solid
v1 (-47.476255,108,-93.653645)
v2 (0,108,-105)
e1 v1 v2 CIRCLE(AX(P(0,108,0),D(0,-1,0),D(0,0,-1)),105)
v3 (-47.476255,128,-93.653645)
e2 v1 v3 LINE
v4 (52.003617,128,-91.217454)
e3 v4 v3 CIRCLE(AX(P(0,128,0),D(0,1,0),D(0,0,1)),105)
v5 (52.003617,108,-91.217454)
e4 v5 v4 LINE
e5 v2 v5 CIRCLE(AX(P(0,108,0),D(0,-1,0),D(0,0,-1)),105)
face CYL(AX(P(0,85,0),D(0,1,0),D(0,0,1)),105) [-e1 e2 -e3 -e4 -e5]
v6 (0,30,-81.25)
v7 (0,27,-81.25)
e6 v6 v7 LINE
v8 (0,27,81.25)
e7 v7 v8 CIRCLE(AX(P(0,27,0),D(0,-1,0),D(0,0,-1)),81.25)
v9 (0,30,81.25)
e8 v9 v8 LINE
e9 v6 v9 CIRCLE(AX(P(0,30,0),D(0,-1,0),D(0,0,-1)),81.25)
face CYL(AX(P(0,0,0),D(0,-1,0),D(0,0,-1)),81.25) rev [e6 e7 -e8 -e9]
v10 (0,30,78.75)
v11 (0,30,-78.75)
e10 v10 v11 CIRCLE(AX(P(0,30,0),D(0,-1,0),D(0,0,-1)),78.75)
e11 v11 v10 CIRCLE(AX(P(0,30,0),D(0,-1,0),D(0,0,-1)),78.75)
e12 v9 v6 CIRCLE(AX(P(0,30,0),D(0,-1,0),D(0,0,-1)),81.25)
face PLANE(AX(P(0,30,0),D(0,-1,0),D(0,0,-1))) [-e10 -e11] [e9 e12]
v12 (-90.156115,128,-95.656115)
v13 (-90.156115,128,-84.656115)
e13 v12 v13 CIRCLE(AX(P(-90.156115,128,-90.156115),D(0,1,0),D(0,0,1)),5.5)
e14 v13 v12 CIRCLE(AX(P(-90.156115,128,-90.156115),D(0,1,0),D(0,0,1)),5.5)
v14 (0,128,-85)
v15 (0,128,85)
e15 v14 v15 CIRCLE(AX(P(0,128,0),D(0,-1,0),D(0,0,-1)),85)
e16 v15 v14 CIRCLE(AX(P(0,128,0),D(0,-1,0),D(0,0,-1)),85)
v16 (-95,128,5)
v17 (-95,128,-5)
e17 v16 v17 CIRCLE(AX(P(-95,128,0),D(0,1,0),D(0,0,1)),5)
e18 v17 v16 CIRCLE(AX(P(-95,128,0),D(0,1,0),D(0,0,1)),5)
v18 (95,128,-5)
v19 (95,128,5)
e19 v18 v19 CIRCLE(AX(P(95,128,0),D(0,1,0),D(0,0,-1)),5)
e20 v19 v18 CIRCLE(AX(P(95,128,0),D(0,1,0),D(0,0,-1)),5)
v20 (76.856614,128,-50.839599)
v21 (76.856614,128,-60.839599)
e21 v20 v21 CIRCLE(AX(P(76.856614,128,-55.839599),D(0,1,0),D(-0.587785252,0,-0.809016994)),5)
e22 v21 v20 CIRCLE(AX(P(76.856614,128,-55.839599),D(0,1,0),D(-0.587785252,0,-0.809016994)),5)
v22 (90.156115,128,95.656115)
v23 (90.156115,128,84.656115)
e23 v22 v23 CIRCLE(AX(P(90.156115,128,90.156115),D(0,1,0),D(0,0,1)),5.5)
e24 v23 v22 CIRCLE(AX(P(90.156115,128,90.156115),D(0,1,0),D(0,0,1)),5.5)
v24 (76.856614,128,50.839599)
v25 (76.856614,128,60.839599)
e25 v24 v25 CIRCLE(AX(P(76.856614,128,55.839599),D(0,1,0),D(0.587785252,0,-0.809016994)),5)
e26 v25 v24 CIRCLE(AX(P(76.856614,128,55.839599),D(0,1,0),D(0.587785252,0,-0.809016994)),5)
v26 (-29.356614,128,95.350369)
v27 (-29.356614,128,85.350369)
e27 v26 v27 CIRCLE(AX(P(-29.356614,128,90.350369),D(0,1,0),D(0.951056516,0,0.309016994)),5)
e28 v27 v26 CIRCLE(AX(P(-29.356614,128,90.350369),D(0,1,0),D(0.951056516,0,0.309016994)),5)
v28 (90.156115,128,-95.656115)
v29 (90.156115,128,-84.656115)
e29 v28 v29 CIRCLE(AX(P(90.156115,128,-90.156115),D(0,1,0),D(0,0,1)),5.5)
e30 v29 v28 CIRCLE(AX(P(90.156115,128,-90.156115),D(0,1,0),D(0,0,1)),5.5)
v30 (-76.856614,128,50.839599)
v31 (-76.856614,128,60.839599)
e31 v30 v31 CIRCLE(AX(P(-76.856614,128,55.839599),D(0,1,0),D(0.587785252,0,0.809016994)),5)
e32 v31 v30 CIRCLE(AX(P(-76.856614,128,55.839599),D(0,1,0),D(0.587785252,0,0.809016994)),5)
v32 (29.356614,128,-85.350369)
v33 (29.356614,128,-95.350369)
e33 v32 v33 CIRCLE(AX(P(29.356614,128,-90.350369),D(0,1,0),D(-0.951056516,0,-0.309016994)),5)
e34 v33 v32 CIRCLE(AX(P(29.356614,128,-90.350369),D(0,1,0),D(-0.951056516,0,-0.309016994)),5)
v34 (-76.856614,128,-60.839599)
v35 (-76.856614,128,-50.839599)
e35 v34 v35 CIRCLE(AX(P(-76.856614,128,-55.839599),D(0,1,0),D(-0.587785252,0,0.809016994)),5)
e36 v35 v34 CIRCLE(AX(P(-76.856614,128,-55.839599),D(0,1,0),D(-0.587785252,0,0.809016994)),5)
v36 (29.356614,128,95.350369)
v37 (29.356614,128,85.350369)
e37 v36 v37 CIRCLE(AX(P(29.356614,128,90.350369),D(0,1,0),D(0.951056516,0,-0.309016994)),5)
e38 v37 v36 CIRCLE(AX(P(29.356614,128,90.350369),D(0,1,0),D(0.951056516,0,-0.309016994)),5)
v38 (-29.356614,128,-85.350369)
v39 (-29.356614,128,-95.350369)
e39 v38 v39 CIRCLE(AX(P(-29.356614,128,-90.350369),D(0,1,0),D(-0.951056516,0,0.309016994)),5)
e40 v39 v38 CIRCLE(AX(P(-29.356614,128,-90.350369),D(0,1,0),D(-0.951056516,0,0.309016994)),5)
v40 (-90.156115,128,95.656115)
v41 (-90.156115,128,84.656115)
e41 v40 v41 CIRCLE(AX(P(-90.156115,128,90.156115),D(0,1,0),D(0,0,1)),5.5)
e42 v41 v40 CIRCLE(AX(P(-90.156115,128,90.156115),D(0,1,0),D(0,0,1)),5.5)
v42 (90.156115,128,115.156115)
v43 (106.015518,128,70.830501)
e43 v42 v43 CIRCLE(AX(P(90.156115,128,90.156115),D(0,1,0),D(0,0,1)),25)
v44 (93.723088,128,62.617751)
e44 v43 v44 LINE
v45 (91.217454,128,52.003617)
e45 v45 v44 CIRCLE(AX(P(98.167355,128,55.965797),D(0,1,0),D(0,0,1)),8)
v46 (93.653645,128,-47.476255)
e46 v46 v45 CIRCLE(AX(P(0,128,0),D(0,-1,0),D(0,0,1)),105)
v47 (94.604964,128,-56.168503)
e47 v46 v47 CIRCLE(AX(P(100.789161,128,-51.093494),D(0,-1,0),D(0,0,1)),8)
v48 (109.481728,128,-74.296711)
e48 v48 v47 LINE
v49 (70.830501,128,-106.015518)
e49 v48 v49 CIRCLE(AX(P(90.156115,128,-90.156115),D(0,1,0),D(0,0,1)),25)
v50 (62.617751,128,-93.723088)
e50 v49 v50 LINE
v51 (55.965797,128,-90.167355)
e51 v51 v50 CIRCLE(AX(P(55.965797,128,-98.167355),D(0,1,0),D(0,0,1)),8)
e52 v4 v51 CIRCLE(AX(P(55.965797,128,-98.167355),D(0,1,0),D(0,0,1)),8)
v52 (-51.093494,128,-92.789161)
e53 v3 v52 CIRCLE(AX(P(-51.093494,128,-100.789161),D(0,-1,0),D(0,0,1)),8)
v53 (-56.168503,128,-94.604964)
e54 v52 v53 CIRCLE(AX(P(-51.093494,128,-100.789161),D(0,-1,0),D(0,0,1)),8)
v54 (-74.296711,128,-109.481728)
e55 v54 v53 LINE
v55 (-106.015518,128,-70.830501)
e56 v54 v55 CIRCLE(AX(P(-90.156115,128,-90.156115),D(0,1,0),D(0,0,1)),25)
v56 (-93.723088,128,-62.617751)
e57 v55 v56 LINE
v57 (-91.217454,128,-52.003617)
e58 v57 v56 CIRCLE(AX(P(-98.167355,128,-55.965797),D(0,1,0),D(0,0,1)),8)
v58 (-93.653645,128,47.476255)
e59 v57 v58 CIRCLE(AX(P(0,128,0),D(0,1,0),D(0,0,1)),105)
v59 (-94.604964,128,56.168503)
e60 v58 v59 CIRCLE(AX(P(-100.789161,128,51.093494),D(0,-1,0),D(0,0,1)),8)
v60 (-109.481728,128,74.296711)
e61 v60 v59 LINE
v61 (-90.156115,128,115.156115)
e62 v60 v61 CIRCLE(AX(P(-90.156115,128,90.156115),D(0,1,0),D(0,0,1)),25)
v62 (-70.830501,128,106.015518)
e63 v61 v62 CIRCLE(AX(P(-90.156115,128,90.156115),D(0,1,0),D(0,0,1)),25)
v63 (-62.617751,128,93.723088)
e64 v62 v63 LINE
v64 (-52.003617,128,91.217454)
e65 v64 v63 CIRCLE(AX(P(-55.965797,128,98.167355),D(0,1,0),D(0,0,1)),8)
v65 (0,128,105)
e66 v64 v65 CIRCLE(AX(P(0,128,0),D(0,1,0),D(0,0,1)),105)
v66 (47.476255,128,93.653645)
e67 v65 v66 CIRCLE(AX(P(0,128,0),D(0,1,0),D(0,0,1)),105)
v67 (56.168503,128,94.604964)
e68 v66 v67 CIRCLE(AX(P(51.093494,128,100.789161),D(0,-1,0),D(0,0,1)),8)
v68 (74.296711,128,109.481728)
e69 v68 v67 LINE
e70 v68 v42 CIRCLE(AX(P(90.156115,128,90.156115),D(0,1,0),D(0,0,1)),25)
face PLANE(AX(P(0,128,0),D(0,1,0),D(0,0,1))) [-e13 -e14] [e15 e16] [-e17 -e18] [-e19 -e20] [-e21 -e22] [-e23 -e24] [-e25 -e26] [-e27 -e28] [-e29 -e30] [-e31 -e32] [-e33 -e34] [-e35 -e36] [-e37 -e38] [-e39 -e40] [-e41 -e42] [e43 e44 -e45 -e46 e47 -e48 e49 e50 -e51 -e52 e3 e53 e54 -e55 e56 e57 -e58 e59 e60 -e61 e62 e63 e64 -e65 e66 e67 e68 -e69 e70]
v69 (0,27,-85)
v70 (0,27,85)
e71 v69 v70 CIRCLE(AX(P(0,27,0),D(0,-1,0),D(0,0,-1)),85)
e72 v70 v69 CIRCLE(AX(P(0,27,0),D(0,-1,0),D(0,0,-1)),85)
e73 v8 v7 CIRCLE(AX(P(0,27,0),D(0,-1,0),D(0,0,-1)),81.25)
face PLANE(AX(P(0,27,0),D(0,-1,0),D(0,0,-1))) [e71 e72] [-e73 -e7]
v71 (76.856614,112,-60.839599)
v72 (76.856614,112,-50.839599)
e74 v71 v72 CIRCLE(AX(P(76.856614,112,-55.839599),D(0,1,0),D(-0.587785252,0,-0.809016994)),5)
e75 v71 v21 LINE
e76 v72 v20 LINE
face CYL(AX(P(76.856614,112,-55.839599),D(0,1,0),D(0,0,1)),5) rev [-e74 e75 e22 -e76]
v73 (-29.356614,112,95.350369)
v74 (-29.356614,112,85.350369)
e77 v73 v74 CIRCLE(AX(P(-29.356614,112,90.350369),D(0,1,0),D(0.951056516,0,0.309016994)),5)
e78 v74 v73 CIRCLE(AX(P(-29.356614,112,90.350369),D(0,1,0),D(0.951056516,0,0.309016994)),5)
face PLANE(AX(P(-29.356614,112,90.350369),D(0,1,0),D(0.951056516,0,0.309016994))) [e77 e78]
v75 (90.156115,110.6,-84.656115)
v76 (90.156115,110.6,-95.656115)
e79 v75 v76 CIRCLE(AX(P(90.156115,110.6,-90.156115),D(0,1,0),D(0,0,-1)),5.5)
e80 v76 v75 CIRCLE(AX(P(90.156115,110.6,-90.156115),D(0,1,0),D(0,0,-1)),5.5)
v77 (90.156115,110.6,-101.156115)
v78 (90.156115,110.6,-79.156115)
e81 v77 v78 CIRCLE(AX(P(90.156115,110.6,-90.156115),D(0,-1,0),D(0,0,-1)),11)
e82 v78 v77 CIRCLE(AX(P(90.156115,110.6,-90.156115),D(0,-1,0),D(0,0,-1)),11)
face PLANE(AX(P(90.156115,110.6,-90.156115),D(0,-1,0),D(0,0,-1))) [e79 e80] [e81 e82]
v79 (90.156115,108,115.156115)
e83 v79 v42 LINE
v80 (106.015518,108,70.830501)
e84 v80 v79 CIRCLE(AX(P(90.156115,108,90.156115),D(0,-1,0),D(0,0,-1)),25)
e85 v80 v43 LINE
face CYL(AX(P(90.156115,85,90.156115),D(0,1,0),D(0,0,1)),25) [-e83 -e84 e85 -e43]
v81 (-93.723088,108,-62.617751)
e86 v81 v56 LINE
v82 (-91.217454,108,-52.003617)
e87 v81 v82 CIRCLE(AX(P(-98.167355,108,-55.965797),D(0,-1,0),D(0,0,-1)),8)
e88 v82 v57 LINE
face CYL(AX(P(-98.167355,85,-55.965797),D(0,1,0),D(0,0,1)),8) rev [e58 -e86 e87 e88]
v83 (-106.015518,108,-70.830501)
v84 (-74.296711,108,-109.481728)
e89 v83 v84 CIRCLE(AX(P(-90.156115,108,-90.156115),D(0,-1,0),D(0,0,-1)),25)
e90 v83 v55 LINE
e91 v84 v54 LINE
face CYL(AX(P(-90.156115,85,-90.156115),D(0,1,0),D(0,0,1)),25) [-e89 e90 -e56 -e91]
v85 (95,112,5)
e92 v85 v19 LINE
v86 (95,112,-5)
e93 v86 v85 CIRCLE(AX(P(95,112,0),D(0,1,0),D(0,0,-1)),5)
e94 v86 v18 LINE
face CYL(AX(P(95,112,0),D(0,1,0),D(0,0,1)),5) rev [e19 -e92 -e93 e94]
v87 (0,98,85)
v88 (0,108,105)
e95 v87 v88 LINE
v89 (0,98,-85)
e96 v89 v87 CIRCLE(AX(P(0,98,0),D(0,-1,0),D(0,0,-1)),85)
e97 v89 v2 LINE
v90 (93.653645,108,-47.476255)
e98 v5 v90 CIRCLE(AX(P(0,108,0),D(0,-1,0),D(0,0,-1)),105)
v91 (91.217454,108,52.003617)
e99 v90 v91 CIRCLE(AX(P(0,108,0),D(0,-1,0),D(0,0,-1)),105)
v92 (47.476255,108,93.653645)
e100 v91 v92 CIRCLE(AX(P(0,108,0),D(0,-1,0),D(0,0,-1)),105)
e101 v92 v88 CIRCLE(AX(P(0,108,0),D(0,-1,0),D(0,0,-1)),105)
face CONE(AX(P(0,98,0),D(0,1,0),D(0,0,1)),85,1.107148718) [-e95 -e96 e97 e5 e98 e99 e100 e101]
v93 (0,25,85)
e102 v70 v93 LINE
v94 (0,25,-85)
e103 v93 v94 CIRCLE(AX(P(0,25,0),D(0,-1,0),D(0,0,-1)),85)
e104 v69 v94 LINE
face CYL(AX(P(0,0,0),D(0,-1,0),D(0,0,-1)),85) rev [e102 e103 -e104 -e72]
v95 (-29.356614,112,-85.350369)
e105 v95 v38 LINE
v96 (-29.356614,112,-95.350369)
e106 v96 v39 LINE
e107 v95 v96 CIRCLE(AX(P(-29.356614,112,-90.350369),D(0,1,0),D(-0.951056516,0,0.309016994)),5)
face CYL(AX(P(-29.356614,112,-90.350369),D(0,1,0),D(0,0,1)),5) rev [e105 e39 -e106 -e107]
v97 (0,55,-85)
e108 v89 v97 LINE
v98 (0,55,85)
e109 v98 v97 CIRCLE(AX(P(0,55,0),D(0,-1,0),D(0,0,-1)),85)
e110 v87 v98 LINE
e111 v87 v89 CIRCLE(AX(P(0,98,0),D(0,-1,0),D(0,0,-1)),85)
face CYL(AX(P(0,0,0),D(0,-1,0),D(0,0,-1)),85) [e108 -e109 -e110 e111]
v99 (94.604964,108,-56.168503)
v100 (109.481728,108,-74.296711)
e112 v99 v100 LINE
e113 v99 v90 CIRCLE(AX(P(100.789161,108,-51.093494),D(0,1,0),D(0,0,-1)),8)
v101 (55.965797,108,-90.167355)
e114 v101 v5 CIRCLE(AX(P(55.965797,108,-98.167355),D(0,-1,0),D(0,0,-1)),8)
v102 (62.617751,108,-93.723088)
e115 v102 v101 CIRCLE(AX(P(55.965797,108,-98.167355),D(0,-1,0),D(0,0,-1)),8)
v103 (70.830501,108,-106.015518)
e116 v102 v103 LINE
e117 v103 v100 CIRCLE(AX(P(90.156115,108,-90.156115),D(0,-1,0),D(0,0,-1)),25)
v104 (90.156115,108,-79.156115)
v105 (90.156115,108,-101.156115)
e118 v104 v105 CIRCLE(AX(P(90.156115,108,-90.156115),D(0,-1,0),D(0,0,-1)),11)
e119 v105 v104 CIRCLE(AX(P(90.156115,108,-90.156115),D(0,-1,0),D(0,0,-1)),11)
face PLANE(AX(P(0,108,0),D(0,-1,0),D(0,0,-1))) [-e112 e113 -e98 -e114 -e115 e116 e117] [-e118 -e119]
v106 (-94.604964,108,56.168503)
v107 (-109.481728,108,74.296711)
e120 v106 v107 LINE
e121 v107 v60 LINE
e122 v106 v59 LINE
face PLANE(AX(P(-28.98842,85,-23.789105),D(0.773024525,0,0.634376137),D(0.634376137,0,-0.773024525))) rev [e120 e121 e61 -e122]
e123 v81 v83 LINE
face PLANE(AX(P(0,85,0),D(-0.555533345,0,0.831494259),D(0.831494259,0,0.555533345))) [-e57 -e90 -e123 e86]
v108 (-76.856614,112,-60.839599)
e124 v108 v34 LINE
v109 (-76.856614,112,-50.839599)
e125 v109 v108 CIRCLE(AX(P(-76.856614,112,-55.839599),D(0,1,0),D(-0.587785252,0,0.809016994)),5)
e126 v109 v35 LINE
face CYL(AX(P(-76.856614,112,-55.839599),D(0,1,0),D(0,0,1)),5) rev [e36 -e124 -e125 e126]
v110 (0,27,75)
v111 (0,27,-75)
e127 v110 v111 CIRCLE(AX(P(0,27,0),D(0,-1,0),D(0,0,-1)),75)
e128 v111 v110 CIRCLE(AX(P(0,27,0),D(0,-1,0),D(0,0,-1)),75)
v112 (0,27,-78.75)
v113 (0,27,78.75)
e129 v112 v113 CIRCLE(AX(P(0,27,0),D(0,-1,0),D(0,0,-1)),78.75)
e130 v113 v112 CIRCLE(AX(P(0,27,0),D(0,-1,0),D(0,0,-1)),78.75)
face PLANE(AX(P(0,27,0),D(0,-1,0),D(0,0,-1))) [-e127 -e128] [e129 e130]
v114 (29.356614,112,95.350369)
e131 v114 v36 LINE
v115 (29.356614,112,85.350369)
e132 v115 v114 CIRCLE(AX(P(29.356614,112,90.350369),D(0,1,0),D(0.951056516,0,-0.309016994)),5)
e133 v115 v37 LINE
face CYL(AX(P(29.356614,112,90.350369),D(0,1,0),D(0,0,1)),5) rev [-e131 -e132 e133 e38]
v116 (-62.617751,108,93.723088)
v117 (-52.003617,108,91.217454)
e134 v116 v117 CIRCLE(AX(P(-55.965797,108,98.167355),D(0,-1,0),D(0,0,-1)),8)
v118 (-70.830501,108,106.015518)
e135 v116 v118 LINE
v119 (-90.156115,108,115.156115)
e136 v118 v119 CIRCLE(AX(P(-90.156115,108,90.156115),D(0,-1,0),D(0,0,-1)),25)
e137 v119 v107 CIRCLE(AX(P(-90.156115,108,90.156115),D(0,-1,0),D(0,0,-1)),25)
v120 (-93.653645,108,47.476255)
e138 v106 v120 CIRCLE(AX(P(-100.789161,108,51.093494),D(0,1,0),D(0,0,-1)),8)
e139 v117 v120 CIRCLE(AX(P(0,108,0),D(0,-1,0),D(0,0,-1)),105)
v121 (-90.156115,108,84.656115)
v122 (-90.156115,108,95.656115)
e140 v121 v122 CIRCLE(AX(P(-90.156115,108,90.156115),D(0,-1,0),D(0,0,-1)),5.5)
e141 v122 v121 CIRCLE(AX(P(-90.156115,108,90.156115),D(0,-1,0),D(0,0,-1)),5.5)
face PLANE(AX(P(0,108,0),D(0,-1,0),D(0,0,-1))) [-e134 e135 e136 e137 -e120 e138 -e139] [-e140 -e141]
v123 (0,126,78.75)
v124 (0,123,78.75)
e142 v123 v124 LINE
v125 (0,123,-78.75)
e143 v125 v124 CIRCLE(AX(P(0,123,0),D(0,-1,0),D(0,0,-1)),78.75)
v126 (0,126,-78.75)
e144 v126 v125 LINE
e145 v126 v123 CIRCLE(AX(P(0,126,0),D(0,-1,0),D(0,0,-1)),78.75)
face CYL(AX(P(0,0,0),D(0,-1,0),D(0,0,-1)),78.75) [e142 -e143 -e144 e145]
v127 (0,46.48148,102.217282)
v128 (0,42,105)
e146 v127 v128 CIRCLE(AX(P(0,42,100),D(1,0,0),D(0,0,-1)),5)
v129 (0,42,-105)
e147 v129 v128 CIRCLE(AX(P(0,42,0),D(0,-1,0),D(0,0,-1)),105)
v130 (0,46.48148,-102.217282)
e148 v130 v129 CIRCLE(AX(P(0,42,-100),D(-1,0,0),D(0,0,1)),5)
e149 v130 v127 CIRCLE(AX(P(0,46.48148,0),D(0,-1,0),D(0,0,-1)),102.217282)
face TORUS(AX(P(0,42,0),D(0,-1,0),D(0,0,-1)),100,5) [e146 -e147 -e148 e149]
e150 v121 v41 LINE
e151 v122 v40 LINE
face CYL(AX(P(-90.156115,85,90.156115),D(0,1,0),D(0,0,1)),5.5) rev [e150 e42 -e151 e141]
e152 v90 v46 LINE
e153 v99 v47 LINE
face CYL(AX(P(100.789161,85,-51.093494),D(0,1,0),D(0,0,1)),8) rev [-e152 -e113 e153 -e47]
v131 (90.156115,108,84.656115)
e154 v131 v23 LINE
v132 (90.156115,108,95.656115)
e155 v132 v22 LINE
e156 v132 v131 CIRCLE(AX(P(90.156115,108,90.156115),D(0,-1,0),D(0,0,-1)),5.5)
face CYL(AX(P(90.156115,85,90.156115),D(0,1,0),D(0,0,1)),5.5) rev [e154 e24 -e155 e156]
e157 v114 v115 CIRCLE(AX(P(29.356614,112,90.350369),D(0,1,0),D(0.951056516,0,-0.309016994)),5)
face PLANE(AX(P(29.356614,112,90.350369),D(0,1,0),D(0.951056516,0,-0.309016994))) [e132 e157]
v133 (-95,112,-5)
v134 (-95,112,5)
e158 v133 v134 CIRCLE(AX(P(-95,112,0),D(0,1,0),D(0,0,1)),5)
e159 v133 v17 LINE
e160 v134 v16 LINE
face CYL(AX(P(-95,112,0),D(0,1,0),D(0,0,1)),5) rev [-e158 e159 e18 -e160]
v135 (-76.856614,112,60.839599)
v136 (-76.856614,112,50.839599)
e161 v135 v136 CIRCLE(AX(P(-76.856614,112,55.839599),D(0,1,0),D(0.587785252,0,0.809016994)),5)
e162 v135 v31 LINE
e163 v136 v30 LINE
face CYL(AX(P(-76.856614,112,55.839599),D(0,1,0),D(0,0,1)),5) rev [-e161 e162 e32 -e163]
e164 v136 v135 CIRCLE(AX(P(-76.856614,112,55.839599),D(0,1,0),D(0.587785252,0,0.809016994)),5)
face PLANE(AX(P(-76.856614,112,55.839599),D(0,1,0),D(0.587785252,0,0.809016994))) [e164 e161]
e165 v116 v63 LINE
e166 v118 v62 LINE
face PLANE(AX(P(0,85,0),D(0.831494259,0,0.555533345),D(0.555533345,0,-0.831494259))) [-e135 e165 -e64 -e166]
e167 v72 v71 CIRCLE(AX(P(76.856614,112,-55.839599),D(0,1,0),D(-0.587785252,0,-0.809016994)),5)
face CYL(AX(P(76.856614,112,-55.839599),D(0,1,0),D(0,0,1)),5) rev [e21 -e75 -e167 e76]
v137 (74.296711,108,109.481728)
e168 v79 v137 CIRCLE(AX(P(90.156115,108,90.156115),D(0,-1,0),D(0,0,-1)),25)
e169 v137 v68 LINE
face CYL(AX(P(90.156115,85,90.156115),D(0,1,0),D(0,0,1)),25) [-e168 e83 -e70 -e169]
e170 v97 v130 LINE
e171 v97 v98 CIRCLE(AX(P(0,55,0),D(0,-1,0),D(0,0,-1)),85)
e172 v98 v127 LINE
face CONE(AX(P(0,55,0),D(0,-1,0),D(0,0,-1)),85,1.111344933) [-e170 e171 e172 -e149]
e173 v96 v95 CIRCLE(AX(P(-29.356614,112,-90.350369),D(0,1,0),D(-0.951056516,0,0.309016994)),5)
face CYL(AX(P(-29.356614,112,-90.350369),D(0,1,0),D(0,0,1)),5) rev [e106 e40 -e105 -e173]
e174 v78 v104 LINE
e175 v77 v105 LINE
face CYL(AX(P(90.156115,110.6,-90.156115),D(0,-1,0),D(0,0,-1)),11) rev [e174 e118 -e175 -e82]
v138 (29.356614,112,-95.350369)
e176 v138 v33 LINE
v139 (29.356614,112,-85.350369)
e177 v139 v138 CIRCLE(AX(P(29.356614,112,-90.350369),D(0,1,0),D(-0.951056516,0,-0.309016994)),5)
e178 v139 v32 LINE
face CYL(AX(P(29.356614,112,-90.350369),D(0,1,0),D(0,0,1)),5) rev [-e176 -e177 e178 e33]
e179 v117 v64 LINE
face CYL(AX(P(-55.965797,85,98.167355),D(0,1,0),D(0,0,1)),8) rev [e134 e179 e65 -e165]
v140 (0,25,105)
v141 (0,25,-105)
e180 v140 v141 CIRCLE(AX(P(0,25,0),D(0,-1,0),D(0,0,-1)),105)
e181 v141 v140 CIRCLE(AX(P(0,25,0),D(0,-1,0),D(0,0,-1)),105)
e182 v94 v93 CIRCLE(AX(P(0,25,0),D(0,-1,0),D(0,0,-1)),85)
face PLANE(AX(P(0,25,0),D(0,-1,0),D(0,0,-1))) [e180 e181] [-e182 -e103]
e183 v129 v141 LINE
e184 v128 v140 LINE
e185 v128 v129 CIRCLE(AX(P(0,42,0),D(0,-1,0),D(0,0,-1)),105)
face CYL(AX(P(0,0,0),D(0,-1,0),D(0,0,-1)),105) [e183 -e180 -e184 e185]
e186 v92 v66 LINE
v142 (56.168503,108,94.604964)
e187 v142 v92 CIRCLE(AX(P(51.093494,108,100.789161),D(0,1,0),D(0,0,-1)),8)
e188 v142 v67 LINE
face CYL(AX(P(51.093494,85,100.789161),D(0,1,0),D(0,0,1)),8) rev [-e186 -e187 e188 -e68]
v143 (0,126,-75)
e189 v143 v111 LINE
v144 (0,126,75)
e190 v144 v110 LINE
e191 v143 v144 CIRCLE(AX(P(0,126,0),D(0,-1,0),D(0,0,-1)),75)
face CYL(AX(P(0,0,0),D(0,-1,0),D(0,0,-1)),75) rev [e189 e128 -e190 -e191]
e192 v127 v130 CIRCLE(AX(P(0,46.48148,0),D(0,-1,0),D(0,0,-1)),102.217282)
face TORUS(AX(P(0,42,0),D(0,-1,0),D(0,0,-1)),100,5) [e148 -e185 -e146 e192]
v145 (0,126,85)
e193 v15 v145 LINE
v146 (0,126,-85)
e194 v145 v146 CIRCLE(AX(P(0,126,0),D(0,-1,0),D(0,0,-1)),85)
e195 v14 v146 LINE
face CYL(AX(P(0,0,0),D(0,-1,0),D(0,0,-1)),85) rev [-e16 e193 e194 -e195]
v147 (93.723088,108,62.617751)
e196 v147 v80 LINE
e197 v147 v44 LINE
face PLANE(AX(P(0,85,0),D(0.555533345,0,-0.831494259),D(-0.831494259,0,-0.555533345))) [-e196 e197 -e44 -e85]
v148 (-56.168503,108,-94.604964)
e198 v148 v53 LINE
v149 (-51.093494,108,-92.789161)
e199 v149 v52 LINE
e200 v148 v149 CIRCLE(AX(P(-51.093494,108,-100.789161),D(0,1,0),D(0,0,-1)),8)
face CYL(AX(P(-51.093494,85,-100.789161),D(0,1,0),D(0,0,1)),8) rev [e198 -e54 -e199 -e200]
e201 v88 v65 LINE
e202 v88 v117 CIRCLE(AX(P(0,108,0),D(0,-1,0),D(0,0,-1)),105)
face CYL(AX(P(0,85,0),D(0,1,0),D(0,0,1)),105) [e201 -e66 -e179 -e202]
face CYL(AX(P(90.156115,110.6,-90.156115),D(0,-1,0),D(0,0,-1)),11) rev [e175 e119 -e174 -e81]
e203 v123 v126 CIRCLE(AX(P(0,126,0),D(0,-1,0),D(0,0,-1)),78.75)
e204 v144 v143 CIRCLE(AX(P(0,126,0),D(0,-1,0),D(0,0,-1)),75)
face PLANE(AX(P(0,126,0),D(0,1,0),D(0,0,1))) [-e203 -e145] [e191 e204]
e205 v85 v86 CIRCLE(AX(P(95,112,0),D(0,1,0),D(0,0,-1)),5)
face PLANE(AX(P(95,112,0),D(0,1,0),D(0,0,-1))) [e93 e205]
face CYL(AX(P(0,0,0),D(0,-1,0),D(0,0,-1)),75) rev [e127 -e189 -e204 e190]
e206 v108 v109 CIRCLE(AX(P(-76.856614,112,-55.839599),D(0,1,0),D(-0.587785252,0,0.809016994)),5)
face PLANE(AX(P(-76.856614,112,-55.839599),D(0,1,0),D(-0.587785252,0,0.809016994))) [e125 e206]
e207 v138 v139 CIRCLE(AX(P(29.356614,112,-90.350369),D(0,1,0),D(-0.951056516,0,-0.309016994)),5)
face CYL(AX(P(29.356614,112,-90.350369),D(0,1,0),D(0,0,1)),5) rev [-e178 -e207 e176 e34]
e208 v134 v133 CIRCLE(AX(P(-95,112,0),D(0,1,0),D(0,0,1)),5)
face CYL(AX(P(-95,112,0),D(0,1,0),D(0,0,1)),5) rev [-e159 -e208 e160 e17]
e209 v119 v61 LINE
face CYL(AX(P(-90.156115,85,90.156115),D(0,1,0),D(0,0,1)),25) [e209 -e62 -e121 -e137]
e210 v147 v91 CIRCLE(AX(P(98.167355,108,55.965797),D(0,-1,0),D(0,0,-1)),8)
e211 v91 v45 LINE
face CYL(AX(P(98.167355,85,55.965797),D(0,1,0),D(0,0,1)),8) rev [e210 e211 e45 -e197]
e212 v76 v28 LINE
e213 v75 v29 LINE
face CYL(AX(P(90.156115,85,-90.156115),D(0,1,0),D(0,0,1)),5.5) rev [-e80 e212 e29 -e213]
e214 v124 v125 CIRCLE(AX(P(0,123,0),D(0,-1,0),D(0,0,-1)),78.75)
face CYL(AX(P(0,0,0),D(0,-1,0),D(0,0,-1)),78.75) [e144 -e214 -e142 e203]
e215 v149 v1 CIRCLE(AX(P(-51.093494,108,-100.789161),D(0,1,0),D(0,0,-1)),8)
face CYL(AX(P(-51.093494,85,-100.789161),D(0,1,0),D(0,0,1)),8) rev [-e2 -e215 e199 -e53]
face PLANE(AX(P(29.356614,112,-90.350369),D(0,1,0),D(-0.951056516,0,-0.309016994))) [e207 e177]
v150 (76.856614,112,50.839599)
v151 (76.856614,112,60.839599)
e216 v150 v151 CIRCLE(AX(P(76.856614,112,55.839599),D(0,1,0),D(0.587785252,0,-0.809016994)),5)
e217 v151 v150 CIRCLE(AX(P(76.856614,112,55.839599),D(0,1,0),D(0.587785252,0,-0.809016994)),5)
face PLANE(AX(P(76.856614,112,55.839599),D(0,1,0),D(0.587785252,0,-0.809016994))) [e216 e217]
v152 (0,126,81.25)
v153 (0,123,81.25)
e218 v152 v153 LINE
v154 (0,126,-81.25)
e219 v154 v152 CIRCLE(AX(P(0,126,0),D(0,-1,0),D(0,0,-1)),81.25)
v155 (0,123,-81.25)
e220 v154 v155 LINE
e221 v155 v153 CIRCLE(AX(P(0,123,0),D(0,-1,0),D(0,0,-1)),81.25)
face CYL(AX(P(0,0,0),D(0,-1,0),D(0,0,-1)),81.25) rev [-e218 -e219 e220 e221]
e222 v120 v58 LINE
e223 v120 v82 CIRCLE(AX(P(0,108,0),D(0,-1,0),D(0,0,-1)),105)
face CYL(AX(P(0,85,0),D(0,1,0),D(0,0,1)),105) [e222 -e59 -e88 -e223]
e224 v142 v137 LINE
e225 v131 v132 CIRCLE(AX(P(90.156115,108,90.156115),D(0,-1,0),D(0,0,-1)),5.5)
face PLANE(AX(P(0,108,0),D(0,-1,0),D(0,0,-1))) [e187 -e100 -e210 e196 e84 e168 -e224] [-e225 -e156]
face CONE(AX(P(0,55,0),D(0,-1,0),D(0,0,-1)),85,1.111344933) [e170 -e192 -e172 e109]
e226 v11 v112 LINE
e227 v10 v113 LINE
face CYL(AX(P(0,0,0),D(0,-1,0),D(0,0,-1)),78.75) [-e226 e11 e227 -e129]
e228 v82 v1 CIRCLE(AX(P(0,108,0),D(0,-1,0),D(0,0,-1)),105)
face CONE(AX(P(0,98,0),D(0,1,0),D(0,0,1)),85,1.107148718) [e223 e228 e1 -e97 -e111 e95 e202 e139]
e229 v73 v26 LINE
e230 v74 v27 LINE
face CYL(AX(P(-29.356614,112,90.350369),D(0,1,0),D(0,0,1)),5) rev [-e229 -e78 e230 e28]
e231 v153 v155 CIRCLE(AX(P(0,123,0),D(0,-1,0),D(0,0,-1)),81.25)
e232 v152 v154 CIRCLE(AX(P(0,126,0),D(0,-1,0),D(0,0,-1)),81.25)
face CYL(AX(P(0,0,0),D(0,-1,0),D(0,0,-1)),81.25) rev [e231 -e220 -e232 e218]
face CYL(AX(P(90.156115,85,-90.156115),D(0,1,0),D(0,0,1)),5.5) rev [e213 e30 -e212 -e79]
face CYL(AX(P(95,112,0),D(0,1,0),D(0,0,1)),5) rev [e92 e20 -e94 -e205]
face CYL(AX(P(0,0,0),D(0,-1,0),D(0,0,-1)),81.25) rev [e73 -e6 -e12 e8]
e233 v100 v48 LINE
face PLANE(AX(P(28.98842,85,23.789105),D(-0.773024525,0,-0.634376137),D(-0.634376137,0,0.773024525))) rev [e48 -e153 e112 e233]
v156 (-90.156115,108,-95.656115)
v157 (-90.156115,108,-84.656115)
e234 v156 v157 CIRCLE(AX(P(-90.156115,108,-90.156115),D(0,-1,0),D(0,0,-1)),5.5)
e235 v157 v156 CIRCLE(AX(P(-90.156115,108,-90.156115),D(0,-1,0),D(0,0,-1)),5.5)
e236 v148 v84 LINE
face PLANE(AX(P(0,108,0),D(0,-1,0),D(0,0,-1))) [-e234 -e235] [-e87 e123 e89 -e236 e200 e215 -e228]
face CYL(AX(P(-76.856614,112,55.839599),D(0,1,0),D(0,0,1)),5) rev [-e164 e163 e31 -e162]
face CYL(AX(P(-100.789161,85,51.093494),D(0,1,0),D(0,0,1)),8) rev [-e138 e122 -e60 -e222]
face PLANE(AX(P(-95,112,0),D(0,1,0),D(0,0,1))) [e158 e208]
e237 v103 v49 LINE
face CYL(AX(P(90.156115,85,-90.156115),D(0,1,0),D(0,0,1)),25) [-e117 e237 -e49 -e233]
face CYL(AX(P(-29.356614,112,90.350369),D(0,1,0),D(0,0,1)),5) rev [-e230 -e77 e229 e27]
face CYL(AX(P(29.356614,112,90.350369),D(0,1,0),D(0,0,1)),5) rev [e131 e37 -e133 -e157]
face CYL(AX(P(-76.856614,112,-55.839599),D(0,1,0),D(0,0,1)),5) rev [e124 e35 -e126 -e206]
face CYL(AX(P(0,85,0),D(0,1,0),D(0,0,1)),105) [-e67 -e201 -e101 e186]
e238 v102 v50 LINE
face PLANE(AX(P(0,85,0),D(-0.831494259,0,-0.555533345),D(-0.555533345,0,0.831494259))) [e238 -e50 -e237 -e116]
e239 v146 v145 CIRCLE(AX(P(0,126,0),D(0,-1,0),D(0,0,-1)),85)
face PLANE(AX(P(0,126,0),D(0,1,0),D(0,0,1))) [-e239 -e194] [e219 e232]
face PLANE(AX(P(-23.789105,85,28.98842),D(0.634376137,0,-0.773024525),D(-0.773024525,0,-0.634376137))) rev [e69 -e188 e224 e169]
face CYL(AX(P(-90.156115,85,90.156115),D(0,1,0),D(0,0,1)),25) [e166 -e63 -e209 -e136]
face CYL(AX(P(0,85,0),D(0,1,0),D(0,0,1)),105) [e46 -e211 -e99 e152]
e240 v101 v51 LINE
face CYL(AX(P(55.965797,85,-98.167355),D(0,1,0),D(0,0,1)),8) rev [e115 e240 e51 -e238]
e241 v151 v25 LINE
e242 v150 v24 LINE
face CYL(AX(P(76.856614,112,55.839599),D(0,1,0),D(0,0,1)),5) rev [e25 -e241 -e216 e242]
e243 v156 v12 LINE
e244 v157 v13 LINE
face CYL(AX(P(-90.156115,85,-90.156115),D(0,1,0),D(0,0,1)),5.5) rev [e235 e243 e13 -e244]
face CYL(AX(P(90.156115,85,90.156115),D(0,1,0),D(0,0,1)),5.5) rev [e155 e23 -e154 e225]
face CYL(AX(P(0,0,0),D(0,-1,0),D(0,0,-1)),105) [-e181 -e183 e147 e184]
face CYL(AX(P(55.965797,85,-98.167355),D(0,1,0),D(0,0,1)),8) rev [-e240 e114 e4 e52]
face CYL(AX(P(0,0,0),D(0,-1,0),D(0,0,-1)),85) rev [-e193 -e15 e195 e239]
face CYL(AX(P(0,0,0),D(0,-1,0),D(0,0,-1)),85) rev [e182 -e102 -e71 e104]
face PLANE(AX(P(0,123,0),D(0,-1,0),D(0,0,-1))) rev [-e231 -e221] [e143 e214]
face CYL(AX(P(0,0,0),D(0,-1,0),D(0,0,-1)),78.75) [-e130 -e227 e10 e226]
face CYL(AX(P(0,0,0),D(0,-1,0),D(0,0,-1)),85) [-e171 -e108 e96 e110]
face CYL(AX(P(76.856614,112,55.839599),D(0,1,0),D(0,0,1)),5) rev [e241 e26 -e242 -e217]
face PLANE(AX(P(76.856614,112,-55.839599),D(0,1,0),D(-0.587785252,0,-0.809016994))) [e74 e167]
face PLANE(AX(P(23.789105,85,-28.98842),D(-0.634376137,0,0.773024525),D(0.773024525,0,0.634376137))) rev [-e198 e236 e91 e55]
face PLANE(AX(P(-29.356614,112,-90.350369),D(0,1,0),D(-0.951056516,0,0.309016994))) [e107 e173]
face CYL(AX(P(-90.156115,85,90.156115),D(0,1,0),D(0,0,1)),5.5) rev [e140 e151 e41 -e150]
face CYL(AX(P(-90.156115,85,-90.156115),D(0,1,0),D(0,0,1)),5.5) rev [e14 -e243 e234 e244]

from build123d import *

# Parameters (mm, degrees)
SKETCH_2_OUTSIDE_W       = 395.692
SKETCH_2_OUTSIDE_H       = 395.692
CUT_EXTRUDE_1_DEPTH      = 43
SKETCH_2_3_R             = 5.5
SKETCH_2_3_R_2           = 4
CUT_EXTRUDE_2_DEPTH      = 43
SKETCH_3_R               = 5
CUT_EXTRUDE_4_DEPTH      = 16
PATTERN_CIRCULAR_2_COUNT = 10
SKETCH_22_R              = 11
CUT_EXTRUDE_13_DEPTH     = 2.6
CUT_EXTRUDE_17_DEPTH     = 47.2


with BuildPart() as part:
    # 草图1 → 旋转1 (revolve)
    with BuildSketch(Plane(origin=(0, 0, 0), x_dir=(0, 0, -1), z_dir=(1, 0, 0))):
        with BuildLine():
            Line((85, 98), (85, 55))
            Line((85, 55), (102.2172823, 46.481479577))
            ThreePointArc((102.2172823, 46.481479577), (104.247729482, 44.637573553), (105, 42))
            Line((105, 42), (105, 25))
            Line((105, 25), (85, 25))
            Line((85, 25), (85, 27))
            Line((85, 27), (81.25, 27))
            Line((81.25, 27), (81.25, 30))
            Line((81.25, 30), (78.75, 30))
            Line((78.75, 30), (78.75, 27))
            Line((78.75, 27), (75, 27))
            Line((75, 27), (75, 126))
            Line((75, 126), (78.75, 126))
            Line((78.75, 126), (78.75, 123))
            Line((78.75, 123), (80, 123))
            Line((80, 123), (81.25, 123))
            Line((81.25, 123), (81.25, 126))
            Line((81.25, 126), (85, 126))
            Line((85, 126), (85, 128))
            Line((85, 128), (152.5, 128))
            Line((152.5, 128), (152.5, 108))
            Line((152.5, 108), (105, 108))
            Line((105, 108), (85, 98))
        make_face()
    revolve(axis=Axis((0, 0, 0), (0, 1, 0)))

    # 草图2 outside → 切除-拉伸1 (cut)
    with BuildSketch(Plane(origin=(0, 128, 0), x_dir=(1, 0, 0), z_dir=(0, 1, 0))):
        Rectangle(SKETCH_2_OUTSIDE_W, SKETCH_2_OUTSIDE_H)
        with BuildLine():
            Line((106.015518025, -70.830501466), (93.723088078, -62.617751167))
            ThreePointArc((93.723088078, -62.617751167), (90.381359185, -57.803804637), (91.217453609, -52.003616769))
            ThreePointArc((91.217453609, -52.003616769), (96.412361456, -41.589139911), (100.422788605, -30.663716814))
            ThreePointArc((100.422788605, -30.663716814), (103.31433575, -26.569981902), (108.074048689, -25))
            Line((108.074048689, -25), (127.5, -25))
            ThreePointArc((127.5, -25), (152.5, 0), (127.5, 25))
            Line((127.5, 25), (108.074048689, 25))
            ThreePointArc((108.074048689, 25), (103.31433575, 26.569981902), (100.422788605, 30.663716814))
            ThreePointArc((100.422788605, 30.663716814), (97.401647161, 39.216312045), (93.653644879, 47.476255126))
            ThreePointArc((93.653644879, 47.476255126), (92.836646991, 51.963853326), (94.604964476, 56.168502708))
            Line((94.604964476, 56.168502708), (109.481727736, 74.296711178))
            ThreePointArc((109.481727736, 74.296711178), (106.015518025, 109.481727736), (70.830501466, 106.015518025))
            Line((70.830501466, 106.015518025), (62.617751167, 93.723088078))
            ThreePointArc((62.617751167, 93.723088078), (57.803804637, 90.381359185), (52.003616769, 91.217453609))
            ThreePointArc((52.003616769, 91.217453609), (2.570604567, 104.96852858), (-47.476255126, 93.653644879))
            ThreePointArc((-47.476255126, 93.653644879), (-51.963853326, 92.836646991), (-56.168502708, 94.604964476))
            Line((-56.168502708, 94.604964476), (-74.296711178, 109.481727736))
            ThreePointArc((-74.296711178, 109.481727736), (-109.481727736, 106.015518025), (-106.015518025, 70.830501466))
            Line((-106.015518025, 70.830501466), (-93.723088078, 62.617751167))
            ThreePointArc((-93.723088078, 62.617751167), (-90.381359185, 57.803804637), (-91.217453609, 52.003616769))
            ThreePointArc((-91.217453609, 52.003616769), (-96.412361456, 41.589139911), (-100.422788605, 30.663716814))
            ThreePointArc((-100.422788605, 30.663716814), (-103.31433575, 26.569981902), (-108.074048689, 25))
            Line((-108.074048689, 25), (-127.5, 25))
            ThreePointArc((-127.5, 25), (-152.5, 0), (-127.5, -25))
            Line((-127.5, -25), (-108.074048689, -25))
            ThreePointArc((-108.074048689, -25), (-103.31433575, -26.569981902), (-100.422788605, -30.663716814))
            ThreePointArc((-100.422788605, -30.663716814), (-97.401647161, -39.216312045), (-93.653644879, -47.476255126))
            ThreePointArc((-93.653644879, -47.476255126), (-92.836646991, -51.963853326), (-94.604964476, -56.168502708))
            Line((-94.604964476, -56.168502708), (-109.481727736, -74.296711178))
            ThreePointArc((-109.481727736, -74.296711178), (-106.015518025, -109.481727736), (-70.830501466, -106.015518025))
            Line((-70.830501466, -106.015518025), (-62.617751167, -93.723088078))
            ThreePointArc((-62.617751167, -93.723088078), (-57.803804637, -90.381359185), (-52.003616769, -91.217453609))
            ThreePointArc((-52.003616769, -91.217453609), (-2.570604567, -104.96852858), (47.476255126, -93.653644879))
            ThreePointArc((47.476255126, -93.653644879), (51.963853326, -92.836646991), (56.168502708, -94.604964476))
            Line((56.168502708, -94.604964476), (74.296711178, -109.481727736))
            ThreePointArc((74.296711178, -109.481727736), (109.481727736, -106.015518025), (106.015518025, -70.830501466))
        make_face(mode=Mode.SUBTRACT)
    extrude(amount=-CUT_EXTRUDE_1_DEPTH, mode=Mode.SUBTRACT)

    # 草图2<3> → 切除-拉伸2 (cut)
    with BuildSketch(Plane(origin=(0, 128, 0), x_dir=(1, 0, 0), z_dir=(0, 1, 0))):
        with Locations(Location((90.156114601, -90.156114601, 0), (0, 0, 270))):
            Circle(SKETCH_2_3_R)
        with Locations(Location((-90.156114601, -90.156114601, 0), (0, 0, 270))):
            Circle(SKETCH_2_3_R)
        with Locations(Location((-90.156114601, 90.156114601, 0), (0, 0, 270))):
            Circle(SKETCH_2_3_R)
        with Locations(Location((90.156114601, 90.156114601, 0), (0, 0, 270))):
            Circle(SKETCH_2_3_R)
        with Locations(Location((-127.5, 0, 0), (0, 0, 270))):
            Circle(SKETCH_2_3_R_2)
        with Locations(Location((127.5, 0, 0), (0, 0, 270))):
            Circle(SKETCH_2_3_R_2)
    extrude(amount=-CUT_EXTRUDE_2_DEPTH, mode=Mode.SUBTRACT)

    # 草图3 → 切除-拉伸4 (cut)
    with BuildSketch(Plane(origin=(0, 128, 0), x_dir=(1, 0, 0), z_dir=(0, 1, 0))):
        with Locations(Location((-95, 0, 0), (0, 0, 270))):
            Circle(SKETCH_3_R)
    cut_extrude_4 = extrude(amount=-CUT_EXTRUDE_4_DEPTH, mode=Mode.SUBTRACT)

    # 阵列(圆周)2: 切除-拉伸4 ×10 about axis
    pattern_circular_2_axis = Axis((0, 0, 0), (0, 1, 0))
    for i in range(1, PATTERN_CIRCULAR_2_COUNT):
        add(cut_extrude_4.rotate(pattern_circular_2_axis, i * 360 / PATTERN_CIRCULAR_2_COUNT), mode=Mode.SUBTRACT)

    # 草图22 → 切除-拉伸13 (cut)
    with BuildSketch(Plane.XZ.offset(-108)):
        with Locations(Location((90.156114601, -90.156114601, 0), (0, 0, 270))):
            Circle(SKETCH_22_R)
    extrude(amount=-CUT_EXTRUDE_13_DEPTH, mode=Mode.SUBTRACT)

    # 草图24 → 切除-拉伸17 (cut)
    with BuildSketch(Plane(origin=(0, 128, 0), x_dir=(1, 0, 0), z_dir=(0, 1, 0))):
        with BuildLine():
            Line((-100.422788605, 30.663716814), (-181.652372804, 37.940541355))
            Line((-181.652372804, 37.940541355), (-167.948313734, -59.042030524))
            Line((-167.948313734, -59.042030524), (-95.973272696, -42.592615887))
            ThreePointArc((-95.973272696, -42.592615887), (-104.806849937, -6.365862568), (-100.422788605, 30.663716814))
        make_face()
        with BuildLine():
            Line((97.905644994, 37.940541355), (167.274054284, 34.075293925))
            Line((167.274054284, 34.075293925), (170.436529454, -59.042030524))
            Line((170.436529454, -59.042030524), (95.973272696, -42.592615887))
            ThreePointArc((95.973272696, -42.592615887), (104.969786296, -2.518722898), (97.905644994, 37.940541355))
        make_face()
    extrude(amount=-CUT_EXTRUDE_17_DEPTH, mode=Mode.SUBTRACT)


solid = part.part
